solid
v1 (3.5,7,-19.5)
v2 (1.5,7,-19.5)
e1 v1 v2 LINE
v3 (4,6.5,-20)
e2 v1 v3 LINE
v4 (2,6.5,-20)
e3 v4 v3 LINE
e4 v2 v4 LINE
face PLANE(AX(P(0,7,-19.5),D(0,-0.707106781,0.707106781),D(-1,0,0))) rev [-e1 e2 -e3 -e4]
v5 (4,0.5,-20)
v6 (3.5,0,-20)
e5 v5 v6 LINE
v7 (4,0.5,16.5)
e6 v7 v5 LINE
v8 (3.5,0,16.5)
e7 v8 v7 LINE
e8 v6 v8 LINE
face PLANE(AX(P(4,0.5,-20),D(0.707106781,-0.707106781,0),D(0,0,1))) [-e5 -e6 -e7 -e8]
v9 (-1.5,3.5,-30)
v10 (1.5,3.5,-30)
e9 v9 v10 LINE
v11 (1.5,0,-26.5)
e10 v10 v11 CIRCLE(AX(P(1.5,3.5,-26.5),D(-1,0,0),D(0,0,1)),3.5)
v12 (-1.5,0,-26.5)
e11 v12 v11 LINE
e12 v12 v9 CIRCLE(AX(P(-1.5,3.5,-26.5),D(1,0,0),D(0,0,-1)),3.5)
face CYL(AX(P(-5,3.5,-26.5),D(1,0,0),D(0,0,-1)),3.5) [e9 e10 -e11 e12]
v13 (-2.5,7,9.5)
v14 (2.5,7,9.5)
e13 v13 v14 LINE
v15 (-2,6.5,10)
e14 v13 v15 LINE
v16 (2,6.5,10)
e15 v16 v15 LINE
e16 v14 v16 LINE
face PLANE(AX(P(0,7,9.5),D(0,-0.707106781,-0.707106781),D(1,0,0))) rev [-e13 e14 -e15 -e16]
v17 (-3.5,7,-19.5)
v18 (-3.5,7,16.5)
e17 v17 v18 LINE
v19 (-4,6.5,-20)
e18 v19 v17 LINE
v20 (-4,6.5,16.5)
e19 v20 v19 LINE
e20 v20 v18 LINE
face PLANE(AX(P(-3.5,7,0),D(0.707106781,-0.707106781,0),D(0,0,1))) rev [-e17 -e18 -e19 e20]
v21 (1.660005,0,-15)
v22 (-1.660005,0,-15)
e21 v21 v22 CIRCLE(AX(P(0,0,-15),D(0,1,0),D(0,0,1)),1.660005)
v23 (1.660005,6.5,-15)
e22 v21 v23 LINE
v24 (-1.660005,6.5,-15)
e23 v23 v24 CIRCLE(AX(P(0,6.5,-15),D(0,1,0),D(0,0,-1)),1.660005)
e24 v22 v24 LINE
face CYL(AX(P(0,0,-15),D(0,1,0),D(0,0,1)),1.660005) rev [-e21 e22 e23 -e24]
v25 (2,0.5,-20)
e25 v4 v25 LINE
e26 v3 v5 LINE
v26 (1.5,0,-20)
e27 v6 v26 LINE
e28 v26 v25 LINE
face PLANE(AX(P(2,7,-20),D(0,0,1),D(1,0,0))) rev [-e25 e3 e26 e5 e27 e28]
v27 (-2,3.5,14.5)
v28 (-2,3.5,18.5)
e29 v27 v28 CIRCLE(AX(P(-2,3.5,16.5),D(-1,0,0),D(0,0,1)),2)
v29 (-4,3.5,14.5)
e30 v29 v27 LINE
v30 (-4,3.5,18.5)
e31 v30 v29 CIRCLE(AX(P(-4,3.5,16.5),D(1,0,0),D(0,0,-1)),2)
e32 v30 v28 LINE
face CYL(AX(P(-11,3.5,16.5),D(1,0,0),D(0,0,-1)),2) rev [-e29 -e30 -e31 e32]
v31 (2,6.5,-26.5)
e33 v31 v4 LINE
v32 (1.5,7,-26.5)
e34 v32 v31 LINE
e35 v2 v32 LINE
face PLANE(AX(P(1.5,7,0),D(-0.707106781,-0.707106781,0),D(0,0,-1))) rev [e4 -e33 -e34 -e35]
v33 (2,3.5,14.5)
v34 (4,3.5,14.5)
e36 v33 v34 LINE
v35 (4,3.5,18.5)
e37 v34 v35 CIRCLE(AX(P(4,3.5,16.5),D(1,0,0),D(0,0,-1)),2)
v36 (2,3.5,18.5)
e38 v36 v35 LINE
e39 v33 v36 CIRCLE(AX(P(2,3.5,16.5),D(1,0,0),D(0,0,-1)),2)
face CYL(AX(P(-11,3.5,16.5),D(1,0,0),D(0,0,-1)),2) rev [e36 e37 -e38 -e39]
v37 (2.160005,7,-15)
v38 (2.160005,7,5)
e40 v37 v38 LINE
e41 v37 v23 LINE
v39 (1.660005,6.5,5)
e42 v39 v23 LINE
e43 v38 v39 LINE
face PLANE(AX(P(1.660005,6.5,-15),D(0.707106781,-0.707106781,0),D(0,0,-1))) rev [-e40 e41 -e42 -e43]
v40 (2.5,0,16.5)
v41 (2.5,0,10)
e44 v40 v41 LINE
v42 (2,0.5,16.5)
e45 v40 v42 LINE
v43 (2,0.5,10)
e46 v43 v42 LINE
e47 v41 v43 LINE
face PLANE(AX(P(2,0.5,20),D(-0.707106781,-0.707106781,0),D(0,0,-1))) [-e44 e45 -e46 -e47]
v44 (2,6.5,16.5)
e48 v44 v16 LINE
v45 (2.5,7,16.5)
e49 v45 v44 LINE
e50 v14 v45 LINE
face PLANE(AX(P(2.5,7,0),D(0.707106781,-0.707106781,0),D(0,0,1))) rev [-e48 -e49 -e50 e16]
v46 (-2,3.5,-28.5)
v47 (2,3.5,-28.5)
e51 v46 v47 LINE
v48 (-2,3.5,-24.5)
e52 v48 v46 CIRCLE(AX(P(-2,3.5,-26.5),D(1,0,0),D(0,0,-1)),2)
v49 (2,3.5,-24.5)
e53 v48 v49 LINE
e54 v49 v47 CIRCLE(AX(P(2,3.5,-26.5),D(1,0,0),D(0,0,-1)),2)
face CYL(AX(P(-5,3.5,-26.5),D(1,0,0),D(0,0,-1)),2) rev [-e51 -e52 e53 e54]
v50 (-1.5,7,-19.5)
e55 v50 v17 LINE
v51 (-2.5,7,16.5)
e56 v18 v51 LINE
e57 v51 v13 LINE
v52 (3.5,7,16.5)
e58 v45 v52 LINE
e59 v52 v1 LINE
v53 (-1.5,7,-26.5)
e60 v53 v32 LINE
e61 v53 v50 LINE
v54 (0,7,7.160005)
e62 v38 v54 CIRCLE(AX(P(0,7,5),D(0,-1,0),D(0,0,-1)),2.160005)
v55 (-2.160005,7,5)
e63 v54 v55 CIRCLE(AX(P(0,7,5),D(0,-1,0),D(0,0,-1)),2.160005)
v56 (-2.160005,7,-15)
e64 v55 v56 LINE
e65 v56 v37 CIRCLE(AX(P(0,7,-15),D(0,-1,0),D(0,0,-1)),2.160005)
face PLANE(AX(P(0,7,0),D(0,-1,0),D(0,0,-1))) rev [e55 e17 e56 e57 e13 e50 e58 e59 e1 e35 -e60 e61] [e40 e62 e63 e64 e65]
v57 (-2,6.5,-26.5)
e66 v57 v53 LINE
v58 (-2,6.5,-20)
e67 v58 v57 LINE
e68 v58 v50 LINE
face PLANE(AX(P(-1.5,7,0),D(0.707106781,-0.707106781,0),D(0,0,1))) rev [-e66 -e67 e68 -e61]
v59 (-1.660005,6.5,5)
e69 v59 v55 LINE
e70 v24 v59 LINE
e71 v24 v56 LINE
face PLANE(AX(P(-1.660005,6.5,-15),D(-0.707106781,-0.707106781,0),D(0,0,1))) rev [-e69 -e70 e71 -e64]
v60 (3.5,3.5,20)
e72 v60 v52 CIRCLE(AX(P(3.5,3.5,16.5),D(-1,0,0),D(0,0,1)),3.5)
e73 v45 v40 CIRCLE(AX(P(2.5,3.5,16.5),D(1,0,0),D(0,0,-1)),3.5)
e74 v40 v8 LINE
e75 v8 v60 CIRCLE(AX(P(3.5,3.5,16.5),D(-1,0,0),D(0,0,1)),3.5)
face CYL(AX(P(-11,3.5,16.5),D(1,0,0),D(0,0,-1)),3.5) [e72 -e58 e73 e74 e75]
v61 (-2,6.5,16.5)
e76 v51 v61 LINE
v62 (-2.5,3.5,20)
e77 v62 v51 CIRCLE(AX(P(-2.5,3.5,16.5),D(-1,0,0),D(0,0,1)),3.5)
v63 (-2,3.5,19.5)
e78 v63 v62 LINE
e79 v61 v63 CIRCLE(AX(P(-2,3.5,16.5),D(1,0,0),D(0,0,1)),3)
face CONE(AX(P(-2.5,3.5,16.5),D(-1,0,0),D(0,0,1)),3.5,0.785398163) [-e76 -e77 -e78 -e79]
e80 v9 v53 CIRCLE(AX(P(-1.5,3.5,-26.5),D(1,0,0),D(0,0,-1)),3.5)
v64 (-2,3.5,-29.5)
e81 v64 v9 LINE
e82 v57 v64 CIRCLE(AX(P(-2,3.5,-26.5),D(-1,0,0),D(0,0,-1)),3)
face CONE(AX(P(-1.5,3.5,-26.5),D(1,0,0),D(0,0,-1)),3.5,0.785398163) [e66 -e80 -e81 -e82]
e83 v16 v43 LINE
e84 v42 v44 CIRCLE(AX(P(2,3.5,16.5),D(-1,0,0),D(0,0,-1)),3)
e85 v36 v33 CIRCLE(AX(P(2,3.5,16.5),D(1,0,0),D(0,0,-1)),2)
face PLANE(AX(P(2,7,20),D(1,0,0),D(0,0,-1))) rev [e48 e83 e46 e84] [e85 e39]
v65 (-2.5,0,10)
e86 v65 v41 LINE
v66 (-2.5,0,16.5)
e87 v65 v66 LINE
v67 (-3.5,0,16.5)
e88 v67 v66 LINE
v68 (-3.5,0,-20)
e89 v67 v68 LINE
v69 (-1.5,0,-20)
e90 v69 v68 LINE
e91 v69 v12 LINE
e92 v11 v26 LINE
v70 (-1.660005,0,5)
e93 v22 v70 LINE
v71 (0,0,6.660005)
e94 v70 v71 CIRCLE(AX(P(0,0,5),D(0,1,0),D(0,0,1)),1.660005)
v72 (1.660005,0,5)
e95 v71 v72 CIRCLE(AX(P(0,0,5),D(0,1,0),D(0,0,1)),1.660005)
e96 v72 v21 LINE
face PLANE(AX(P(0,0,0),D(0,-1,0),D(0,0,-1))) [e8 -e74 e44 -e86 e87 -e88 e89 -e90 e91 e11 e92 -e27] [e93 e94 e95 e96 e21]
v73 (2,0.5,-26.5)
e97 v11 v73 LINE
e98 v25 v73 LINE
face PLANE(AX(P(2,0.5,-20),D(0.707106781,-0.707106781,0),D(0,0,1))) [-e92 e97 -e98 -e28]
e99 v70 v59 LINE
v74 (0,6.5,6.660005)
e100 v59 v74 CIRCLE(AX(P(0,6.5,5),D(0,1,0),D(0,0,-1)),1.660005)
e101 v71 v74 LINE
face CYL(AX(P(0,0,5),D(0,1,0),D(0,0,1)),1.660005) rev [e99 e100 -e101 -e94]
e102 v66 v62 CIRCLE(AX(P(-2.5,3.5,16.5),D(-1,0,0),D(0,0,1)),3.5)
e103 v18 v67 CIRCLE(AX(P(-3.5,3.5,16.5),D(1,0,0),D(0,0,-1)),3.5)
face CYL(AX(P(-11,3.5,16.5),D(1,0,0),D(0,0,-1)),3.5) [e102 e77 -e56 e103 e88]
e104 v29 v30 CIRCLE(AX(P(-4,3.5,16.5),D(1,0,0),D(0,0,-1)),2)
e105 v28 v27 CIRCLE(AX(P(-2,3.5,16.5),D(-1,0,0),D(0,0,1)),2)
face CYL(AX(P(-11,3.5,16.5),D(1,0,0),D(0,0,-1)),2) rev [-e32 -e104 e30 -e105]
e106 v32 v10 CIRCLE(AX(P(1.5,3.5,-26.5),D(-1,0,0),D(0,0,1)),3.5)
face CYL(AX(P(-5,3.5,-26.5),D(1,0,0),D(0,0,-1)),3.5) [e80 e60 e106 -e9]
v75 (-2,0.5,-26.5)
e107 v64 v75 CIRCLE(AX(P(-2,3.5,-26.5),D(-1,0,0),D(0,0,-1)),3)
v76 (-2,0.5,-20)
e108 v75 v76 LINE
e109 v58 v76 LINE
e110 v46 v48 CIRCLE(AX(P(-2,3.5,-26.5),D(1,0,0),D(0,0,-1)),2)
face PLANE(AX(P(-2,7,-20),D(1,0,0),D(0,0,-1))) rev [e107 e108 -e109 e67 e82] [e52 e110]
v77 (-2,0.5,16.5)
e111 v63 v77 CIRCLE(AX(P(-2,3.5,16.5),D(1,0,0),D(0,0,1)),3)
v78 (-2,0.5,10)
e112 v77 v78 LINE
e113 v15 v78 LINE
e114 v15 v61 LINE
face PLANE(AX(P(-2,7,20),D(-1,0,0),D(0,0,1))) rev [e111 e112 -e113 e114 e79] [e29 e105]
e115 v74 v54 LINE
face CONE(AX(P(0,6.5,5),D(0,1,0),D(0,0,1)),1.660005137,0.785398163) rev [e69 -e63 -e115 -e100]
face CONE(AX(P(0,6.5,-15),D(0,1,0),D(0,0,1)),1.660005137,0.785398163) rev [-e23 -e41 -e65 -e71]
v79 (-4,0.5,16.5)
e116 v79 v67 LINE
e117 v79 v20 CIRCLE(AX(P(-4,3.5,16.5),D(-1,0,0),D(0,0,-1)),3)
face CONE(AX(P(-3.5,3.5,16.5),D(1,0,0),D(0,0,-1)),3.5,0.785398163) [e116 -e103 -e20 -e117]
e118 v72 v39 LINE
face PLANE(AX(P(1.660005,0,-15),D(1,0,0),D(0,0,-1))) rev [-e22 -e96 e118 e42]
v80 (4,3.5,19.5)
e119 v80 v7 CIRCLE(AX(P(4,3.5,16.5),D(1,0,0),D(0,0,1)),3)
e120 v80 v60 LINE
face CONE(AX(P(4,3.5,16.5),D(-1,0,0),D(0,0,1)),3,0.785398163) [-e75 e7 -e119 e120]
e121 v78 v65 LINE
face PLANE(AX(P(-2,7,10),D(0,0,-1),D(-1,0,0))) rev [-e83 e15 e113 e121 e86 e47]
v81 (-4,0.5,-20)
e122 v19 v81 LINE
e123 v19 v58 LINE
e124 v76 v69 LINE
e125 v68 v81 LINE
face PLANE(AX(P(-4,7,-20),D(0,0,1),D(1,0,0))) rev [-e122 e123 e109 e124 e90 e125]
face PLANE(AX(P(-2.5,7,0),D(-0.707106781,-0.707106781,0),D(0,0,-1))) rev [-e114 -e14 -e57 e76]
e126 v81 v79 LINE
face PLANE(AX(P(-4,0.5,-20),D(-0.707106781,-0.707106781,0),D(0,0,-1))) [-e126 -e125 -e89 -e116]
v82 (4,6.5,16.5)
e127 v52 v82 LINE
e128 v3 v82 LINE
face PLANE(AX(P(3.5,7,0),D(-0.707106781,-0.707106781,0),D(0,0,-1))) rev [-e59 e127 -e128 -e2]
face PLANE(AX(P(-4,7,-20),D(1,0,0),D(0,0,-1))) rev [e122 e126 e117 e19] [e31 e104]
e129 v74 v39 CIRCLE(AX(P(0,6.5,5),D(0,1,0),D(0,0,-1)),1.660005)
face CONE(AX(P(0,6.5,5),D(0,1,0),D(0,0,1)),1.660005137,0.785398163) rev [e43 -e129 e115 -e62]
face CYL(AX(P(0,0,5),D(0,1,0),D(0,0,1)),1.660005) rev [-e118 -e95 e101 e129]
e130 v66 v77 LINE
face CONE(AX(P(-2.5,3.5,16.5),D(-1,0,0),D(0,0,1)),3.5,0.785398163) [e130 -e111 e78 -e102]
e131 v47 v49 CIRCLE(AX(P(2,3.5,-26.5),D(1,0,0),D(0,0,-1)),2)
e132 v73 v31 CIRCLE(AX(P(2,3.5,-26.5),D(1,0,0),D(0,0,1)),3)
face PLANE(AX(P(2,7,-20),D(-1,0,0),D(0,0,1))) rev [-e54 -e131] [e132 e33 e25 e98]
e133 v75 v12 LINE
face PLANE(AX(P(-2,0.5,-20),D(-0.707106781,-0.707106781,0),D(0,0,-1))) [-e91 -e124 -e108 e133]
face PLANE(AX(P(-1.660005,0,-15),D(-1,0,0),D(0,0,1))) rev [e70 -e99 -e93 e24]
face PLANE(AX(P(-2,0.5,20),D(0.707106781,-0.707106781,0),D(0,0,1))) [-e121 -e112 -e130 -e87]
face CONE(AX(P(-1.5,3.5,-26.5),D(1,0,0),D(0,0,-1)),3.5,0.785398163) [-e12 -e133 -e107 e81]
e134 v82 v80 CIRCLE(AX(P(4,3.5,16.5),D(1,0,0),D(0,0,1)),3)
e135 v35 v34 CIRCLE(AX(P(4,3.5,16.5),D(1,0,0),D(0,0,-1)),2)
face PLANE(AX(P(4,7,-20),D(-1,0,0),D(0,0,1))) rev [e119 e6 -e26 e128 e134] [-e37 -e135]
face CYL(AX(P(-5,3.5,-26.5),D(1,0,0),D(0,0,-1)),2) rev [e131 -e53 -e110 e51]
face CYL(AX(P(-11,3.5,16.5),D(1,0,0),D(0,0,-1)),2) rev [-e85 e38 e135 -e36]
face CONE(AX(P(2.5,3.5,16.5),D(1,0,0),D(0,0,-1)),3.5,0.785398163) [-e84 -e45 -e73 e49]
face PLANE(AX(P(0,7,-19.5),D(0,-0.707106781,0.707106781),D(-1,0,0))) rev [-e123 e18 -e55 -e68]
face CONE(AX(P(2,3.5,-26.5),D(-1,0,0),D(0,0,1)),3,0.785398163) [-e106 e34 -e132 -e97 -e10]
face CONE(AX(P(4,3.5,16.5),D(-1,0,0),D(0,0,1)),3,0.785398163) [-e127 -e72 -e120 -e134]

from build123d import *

# Parameters (mm, degrees)
BOSS_EXTRUDE1_DEPTH = 14
SKETCH2_R           = 4
CUT_EXTRUDE1_DEPTH  = 14
SKETCH3_R           = 4
CUT_EXTRUDE2_DEPTH  = 30
CUT_EXTRUDE3_DEPTH  = 14
CHAMFER1_SIZE       = 1
SCALE1_SCALE        = 0.5


with BuildPart() as part:
    # Sketch1 → Boss-Extrude1 (new body)
    with BuildSketch(Plane(origin=(0, 0, 0), x_dir=(1, 0, 0), z_dir=(0, 1, 0))):
        Polygon((4, 40), (8, 40), (8, -40), (4, -40), (4, -20), (-4, -20), (-4, -40), (-8, -40), (-8, 40), (-4, 40), (-4, 60), (4, 60), align=None)
    extrude(amount=BOSS_EXTRUDE1_DEPTH)

    # Sketch2 → Cut-Extrude1 (cut)
    with BuildSketch(Plane(origin=(4, 0, 0), x_dir=(0, 0, -1), z_dir=(1, 0, 0))):
        with BuildLine():
            Line((60, 14), (53, 14))
            ThreePointArc((53, 14), (57.949747468, 11.949747468), (60, 7))
            Line((60, 7), (60, 14))
        make_face()
        with BuildLine():
            Line((60, 0), (60, 7))
            ThreePointArc((60, 7), (57.949747468, 2.050252532), (53, 0))
            Line((53, 0), (60, 0))
        make_face()
        with Locations((53, 7)):
            Circle(SKETCH2_R)
    extrude(amount=-CUT_EXTRUDE1_DEPTH, mode=Mode.SUBTRACT)

    # Sketch3 → Cut-Extrude2 (cut)
    with BuildSketch(Plane(origin=(8, 0, 0), x_dir=(0, 0, -1), z_dir=(1, 0, 0))):
        with BuildLine():
            ThreePointArc((-40, 7), (-37.949747468, 11.949747468), (-33, 14))
            Line((-33, 14), (-40, 14))
            Line((-40, 14), (-40, 7))
        make_face()
        with BuildLine():
            ThreePointArc((-33, 0), (-37.949747468, 2.050252532), (-40, 7))
            Line((-40, 7), (-40, 0))
            Line((-40, 0), (-33, 0))
        make_face()
        with Locations((-33, 7)):
            Circle(SKETCH3_R)
    extrude(amount=-CUT_EXTRUDE2_DEPTH, mode=Mode.SUBTRACT)

    # Sketch4 → Cut-Extrude3 (cut)
    with BuildSketch(Plane(origin=(0, 14, 0), x_dir=(1, 0, 0), z_dir=(0, 1, 0))):
        with BuildLine():
            Line((3.320010274, 30), (3.320010274, -10))
            ThreePointArc((3.320010274, -10), (0, -13.320010274), (-3.320010274, -10))
            Line((-3.320010274, -10), (-3.320010274, 30))
            ThreePointArc((-3.320010274, 30), (0, 33.320010274), (3.320010274, 30))
        make_face()
    extrude(amount=-CUT_EXTRUDE3_DEPTH, mode=Mode.SUBTRACT)

    # Chamfer1
    chamfer1_edges = [part.edges().sort_by_distance(p)[0] for p in [
        (6, 14, -40),
        (4, 0, 26.5),
        (-8, 0, -3.5),
        (4, 14, -46.5),
        (4, 0, -46.5),
        (0, 14, -33.320010274),
        (-3.320010274, 14, -10),
        (0, 14, 13.320010274),
        (3.320010274, 14, -10),
        (-6, 14, -40),
        (-8, 14, -3.5),
        (0, 14, 20),
        (-4, 14, -46.5),
        (4, 14, 26.5),
        (4, 7, -60),
        (-4, 7, -60),
        (-4, 0, -46.5),
        (4, 7, 40),
        (-4, 14, 26.5),
        (8, 14, -3.5),
        (-8, 7, 40),
        (8, 7, 40),
        (-4, 7, 40),
        (8, 0, -3.5),
        (-4, 0, 26.5),
    ]]
    chamfer(chamfer1_edges, length=CHAMFER1_SIZE)


with BuildPart() as part_1:
    # Scale1: scaled about (0, 0, 0)
    add(part.part.scale(SCALE1_SCALE))


solid = part_1.part
